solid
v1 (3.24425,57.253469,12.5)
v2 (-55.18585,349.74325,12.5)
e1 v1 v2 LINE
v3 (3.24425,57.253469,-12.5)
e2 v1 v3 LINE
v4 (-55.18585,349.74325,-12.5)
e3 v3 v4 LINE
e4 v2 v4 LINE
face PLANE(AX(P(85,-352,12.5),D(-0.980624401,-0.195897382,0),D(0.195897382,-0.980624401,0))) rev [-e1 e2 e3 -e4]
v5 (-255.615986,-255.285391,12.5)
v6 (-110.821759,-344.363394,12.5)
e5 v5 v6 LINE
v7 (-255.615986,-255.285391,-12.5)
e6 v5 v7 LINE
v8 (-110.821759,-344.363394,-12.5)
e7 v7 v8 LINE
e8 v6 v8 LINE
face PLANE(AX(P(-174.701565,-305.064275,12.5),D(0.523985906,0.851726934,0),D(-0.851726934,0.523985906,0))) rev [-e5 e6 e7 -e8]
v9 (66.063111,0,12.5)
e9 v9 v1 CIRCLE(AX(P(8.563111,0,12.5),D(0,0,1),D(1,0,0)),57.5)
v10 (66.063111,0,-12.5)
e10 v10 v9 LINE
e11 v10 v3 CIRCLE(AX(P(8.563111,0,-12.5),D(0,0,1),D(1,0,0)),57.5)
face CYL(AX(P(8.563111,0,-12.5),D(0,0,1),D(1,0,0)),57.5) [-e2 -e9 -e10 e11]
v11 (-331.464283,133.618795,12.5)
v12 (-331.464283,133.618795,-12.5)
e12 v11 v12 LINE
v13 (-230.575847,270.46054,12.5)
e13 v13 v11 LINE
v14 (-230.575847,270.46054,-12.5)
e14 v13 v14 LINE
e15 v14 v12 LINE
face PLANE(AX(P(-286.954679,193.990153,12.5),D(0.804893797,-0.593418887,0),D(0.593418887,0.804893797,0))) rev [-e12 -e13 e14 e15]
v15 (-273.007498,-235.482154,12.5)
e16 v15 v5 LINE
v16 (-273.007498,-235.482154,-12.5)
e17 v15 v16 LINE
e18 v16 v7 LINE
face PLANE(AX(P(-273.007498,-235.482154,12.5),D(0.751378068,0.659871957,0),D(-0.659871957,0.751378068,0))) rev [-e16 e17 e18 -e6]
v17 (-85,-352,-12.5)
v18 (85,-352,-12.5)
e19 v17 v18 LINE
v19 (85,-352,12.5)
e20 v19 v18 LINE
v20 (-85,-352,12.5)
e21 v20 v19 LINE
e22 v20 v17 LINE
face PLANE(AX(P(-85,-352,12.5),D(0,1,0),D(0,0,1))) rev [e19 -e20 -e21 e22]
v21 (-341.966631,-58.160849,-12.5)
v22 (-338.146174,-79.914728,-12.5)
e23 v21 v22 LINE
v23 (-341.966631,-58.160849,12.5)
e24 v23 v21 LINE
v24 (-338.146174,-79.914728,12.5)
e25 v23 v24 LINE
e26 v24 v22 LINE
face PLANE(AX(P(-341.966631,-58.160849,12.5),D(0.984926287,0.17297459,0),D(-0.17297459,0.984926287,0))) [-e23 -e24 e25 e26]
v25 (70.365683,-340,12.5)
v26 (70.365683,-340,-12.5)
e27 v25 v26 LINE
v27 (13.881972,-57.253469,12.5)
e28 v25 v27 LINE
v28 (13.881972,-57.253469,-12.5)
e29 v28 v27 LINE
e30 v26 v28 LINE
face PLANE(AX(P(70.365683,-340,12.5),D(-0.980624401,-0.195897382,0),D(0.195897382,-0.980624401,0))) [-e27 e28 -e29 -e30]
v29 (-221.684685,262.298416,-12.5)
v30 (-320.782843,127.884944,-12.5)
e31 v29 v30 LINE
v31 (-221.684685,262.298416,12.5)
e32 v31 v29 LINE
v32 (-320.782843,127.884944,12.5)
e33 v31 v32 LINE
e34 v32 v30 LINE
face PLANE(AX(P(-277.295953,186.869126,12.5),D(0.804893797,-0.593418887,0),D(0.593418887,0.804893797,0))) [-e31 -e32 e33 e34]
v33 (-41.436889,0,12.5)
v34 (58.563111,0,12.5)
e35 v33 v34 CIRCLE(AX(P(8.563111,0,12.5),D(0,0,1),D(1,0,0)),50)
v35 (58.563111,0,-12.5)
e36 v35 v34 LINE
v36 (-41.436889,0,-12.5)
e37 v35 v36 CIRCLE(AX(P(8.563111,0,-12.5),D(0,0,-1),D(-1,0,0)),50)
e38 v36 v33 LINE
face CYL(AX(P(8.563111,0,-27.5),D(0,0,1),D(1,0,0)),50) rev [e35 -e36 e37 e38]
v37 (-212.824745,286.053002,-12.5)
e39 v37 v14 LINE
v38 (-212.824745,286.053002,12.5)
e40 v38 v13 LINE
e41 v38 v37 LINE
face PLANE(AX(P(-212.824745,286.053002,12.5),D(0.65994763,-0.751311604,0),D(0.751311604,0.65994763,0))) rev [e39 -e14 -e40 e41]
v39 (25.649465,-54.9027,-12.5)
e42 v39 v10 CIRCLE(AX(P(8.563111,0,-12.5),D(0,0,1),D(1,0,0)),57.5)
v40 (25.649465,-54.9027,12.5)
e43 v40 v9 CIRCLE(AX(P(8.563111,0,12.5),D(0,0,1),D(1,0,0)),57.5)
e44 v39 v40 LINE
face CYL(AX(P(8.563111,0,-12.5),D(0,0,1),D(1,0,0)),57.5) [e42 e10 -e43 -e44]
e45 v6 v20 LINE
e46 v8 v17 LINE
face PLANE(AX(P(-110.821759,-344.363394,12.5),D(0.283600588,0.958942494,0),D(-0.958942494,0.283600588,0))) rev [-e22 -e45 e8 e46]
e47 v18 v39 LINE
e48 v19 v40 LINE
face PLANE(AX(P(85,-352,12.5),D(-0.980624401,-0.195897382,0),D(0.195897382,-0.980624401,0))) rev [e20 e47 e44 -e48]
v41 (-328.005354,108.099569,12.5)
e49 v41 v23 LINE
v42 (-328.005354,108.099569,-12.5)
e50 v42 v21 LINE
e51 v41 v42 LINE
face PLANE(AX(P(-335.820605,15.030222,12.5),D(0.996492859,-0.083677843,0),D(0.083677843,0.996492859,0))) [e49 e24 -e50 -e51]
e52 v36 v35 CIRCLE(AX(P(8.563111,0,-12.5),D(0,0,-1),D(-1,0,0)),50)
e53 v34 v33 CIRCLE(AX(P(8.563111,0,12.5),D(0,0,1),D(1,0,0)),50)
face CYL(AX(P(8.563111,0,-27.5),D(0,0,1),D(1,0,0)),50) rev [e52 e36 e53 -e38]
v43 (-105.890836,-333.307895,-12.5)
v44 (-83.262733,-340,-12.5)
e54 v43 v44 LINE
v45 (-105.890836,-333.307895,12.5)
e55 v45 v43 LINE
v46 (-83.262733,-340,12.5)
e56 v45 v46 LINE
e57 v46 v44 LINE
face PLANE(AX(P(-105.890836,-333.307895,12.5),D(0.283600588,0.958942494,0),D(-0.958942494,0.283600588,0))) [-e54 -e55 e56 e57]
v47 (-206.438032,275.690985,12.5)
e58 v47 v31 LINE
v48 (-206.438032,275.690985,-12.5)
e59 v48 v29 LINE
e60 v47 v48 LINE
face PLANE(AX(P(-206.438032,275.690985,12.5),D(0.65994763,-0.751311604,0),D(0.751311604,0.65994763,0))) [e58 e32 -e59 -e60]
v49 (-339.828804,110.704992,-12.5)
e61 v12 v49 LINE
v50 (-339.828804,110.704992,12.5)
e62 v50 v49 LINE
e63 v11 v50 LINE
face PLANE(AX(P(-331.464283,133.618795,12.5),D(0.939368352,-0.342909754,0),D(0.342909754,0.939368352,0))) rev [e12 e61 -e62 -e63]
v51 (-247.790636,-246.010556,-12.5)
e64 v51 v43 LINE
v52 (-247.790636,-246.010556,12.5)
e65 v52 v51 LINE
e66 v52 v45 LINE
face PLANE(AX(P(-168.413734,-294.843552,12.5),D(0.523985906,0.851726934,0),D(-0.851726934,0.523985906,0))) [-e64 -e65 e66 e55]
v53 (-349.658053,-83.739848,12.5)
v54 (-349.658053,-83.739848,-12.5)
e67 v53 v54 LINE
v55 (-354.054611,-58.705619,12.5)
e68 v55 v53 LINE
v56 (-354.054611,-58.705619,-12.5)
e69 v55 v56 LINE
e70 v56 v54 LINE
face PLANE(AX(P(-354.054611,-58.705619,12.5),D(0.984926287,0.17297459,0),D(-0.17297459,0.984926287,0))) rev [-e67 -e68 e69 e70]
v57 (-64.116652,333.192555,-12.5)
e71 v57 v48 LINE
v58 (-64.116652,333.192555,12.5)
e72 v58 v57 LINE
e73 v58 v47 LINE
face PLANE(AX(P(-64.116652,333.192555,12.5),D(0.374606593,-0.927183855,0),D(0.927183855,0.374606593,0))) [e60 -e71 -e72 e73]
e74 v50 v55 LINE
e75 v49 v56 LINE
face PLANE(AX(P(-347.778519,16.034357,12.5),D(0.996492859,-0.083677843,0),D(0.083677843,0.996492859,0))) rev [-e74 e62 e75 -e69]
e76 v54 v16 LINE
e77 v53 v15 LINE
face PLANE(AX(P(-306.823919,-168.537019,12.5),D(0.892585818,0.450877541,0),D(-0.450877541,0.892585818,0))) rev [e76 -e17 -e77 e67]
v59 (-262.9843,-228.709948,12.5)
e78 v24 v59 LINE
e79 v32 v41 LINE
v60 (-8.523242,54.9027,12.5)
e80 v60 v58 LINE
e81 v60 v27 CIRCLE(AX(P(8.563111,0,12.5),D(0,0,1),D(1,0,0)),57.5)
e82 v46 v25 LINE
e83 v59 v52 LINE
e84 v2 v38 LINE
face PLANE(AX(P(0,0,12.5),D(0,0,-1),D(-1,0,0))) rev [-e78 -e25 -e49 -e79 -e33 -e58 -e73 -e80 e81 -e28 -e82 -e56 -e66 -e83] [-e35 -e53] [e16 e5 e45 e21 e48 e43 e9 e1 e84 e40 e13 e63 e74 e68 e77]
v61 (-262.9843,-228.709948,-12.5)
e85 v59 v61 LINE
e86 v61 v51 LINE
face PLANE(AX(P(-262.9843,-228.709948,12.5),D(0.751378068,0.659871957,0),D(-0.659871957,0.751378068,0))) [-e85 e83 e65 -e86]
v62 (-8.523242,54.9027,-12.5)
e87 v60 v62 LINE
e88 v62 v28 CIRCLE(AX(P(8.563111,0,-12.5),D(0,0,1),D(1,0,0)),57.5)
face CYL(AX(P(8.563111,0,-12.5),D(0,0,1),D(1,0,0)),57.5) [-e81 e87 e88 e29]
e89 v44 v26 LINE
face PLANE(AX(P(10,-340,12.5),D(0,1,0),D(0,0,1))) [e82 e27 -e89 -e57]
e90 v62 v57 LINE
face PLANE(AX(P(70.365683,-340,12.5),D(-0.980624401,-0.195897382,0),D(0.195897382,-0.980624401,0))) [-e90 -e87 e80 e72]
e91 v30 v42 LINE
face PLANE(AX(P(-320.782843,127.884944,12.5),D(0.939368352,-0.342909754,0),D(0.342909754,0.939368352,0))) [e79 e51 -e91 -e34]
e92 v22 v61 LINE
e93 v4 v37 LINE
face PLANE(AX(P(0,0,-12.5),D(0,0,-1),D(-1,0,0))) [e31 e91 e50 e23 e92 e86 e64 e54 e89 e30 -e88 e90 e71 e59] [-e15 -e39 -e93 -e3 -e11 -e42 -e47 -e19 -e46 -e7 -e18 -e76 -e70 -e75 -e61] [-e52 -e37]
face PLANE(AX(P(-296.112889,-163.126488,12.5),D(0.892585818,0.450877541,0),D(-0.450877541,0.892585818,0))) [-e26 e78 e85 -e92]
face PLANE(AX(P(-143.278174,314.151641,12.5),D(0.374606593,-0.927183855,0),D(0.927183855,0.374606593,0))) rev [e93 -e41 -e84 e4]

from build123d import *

# Parameters (mm, degrees)
EXTRUDE_1_DEPTH     = 12.5
SKETCH_3_R          = 50
CUT_EXTRUDE_1_DEPTH = 40
SKETCH_4_R          = 57.5
SKETCH_4_R_2        = 50
EXTRUDE_2_DEPTH     = 25


with BuildPart() as part:
    # 草图1 → 凸台-拉伸1 (new, symmetric)
    with BuildSketch(Plane.XY):
        Polygon((10, -352), (85, -352), (-55.185850126, 349.743250156), (-124.732421354, 321.644611463), (-143.278173681, 314.151641145), (-212.824744909, 286.053002452), (-230.575847037, 270.460540253), (-275.085451102, 210.089181938), (-286.954678853, 193.990153053), (-331.464282918, 133.618794737), (-339.828804089, 110.704991943), (-346.104895164, 35.965016687), (-347.77851945, 16.034356619), (-354.054610525, -58.705618637), (-349.658052524, -83.739847979), (-315.841631523, -150.684982948), (-306.823919256, -168.53701894), (-273.007498256, -235.482153909), (-255.615985839, -255.285391269), (-191.736179852, -294.58451012), (-174.701564922, -305.064275147), (-110.821758935, -344.363393998), (-85, -352), (-10, -352), align=None)
        Polygon((-138.78289456, 303.02543489), (-206.438031879, 275.690985101), (-221.684684581, 262.298416336), (-265.426725534, 202.968155298), (-277.295953285, 186.869126414), (-320.782842839, 127.884944314), (-328.005353759, 108.099568976), (-334.146980853, 34.960882567), (-335.820605139, 15.030222499), (-341.966631122, -58.160848878), (-338.146174396, -79.914727665), (-305.130601702, -145.27445246), (-296.112889435, -163.126488451), (-262.984300248, -228.709947873), (-247.790635751, -246.010556193), (-185.448348981, -284.36378691), (-168.413734051, -294.843551937), (-105.890836047, -333.307895427), (-83.26273254, -340), (-10, -340), (10, -340), (70.365682758, -340), (-64.116651933, 333.192555096), (-120.237142233, 310.518405208), align=None, mode=Mode.SUBTRACT)
    extrude(amount=EXTRUDE_1_DEPTH, both=True)

    # 草图3 → 切除-拉伸1 (cut)
    with BuildSketch(Plane.XY.offset(12.5)):
        with Locations((8.563111146, 0)):
            Circle(SKETCH_3_R)
    extrude(amount=-CUT_EXTRUDE_1_DEPTH, mode=Mode.SUBTRACT)

    # 草图4 → 凸台-拉伸2 (add)
    with BuildSketch(Plane.XY.offset(12.5)):
        with Locations((8.563111146, 0)):
            Circle(SKETCH_4_R)
        with Locations((8.563111146, 0)):
            Circle(SKETCH_4_R_2, mode=Mode.SUBTRACT)
    extrude(amount=-EXTRUDE_2_DEPTH)


solid = part.part
